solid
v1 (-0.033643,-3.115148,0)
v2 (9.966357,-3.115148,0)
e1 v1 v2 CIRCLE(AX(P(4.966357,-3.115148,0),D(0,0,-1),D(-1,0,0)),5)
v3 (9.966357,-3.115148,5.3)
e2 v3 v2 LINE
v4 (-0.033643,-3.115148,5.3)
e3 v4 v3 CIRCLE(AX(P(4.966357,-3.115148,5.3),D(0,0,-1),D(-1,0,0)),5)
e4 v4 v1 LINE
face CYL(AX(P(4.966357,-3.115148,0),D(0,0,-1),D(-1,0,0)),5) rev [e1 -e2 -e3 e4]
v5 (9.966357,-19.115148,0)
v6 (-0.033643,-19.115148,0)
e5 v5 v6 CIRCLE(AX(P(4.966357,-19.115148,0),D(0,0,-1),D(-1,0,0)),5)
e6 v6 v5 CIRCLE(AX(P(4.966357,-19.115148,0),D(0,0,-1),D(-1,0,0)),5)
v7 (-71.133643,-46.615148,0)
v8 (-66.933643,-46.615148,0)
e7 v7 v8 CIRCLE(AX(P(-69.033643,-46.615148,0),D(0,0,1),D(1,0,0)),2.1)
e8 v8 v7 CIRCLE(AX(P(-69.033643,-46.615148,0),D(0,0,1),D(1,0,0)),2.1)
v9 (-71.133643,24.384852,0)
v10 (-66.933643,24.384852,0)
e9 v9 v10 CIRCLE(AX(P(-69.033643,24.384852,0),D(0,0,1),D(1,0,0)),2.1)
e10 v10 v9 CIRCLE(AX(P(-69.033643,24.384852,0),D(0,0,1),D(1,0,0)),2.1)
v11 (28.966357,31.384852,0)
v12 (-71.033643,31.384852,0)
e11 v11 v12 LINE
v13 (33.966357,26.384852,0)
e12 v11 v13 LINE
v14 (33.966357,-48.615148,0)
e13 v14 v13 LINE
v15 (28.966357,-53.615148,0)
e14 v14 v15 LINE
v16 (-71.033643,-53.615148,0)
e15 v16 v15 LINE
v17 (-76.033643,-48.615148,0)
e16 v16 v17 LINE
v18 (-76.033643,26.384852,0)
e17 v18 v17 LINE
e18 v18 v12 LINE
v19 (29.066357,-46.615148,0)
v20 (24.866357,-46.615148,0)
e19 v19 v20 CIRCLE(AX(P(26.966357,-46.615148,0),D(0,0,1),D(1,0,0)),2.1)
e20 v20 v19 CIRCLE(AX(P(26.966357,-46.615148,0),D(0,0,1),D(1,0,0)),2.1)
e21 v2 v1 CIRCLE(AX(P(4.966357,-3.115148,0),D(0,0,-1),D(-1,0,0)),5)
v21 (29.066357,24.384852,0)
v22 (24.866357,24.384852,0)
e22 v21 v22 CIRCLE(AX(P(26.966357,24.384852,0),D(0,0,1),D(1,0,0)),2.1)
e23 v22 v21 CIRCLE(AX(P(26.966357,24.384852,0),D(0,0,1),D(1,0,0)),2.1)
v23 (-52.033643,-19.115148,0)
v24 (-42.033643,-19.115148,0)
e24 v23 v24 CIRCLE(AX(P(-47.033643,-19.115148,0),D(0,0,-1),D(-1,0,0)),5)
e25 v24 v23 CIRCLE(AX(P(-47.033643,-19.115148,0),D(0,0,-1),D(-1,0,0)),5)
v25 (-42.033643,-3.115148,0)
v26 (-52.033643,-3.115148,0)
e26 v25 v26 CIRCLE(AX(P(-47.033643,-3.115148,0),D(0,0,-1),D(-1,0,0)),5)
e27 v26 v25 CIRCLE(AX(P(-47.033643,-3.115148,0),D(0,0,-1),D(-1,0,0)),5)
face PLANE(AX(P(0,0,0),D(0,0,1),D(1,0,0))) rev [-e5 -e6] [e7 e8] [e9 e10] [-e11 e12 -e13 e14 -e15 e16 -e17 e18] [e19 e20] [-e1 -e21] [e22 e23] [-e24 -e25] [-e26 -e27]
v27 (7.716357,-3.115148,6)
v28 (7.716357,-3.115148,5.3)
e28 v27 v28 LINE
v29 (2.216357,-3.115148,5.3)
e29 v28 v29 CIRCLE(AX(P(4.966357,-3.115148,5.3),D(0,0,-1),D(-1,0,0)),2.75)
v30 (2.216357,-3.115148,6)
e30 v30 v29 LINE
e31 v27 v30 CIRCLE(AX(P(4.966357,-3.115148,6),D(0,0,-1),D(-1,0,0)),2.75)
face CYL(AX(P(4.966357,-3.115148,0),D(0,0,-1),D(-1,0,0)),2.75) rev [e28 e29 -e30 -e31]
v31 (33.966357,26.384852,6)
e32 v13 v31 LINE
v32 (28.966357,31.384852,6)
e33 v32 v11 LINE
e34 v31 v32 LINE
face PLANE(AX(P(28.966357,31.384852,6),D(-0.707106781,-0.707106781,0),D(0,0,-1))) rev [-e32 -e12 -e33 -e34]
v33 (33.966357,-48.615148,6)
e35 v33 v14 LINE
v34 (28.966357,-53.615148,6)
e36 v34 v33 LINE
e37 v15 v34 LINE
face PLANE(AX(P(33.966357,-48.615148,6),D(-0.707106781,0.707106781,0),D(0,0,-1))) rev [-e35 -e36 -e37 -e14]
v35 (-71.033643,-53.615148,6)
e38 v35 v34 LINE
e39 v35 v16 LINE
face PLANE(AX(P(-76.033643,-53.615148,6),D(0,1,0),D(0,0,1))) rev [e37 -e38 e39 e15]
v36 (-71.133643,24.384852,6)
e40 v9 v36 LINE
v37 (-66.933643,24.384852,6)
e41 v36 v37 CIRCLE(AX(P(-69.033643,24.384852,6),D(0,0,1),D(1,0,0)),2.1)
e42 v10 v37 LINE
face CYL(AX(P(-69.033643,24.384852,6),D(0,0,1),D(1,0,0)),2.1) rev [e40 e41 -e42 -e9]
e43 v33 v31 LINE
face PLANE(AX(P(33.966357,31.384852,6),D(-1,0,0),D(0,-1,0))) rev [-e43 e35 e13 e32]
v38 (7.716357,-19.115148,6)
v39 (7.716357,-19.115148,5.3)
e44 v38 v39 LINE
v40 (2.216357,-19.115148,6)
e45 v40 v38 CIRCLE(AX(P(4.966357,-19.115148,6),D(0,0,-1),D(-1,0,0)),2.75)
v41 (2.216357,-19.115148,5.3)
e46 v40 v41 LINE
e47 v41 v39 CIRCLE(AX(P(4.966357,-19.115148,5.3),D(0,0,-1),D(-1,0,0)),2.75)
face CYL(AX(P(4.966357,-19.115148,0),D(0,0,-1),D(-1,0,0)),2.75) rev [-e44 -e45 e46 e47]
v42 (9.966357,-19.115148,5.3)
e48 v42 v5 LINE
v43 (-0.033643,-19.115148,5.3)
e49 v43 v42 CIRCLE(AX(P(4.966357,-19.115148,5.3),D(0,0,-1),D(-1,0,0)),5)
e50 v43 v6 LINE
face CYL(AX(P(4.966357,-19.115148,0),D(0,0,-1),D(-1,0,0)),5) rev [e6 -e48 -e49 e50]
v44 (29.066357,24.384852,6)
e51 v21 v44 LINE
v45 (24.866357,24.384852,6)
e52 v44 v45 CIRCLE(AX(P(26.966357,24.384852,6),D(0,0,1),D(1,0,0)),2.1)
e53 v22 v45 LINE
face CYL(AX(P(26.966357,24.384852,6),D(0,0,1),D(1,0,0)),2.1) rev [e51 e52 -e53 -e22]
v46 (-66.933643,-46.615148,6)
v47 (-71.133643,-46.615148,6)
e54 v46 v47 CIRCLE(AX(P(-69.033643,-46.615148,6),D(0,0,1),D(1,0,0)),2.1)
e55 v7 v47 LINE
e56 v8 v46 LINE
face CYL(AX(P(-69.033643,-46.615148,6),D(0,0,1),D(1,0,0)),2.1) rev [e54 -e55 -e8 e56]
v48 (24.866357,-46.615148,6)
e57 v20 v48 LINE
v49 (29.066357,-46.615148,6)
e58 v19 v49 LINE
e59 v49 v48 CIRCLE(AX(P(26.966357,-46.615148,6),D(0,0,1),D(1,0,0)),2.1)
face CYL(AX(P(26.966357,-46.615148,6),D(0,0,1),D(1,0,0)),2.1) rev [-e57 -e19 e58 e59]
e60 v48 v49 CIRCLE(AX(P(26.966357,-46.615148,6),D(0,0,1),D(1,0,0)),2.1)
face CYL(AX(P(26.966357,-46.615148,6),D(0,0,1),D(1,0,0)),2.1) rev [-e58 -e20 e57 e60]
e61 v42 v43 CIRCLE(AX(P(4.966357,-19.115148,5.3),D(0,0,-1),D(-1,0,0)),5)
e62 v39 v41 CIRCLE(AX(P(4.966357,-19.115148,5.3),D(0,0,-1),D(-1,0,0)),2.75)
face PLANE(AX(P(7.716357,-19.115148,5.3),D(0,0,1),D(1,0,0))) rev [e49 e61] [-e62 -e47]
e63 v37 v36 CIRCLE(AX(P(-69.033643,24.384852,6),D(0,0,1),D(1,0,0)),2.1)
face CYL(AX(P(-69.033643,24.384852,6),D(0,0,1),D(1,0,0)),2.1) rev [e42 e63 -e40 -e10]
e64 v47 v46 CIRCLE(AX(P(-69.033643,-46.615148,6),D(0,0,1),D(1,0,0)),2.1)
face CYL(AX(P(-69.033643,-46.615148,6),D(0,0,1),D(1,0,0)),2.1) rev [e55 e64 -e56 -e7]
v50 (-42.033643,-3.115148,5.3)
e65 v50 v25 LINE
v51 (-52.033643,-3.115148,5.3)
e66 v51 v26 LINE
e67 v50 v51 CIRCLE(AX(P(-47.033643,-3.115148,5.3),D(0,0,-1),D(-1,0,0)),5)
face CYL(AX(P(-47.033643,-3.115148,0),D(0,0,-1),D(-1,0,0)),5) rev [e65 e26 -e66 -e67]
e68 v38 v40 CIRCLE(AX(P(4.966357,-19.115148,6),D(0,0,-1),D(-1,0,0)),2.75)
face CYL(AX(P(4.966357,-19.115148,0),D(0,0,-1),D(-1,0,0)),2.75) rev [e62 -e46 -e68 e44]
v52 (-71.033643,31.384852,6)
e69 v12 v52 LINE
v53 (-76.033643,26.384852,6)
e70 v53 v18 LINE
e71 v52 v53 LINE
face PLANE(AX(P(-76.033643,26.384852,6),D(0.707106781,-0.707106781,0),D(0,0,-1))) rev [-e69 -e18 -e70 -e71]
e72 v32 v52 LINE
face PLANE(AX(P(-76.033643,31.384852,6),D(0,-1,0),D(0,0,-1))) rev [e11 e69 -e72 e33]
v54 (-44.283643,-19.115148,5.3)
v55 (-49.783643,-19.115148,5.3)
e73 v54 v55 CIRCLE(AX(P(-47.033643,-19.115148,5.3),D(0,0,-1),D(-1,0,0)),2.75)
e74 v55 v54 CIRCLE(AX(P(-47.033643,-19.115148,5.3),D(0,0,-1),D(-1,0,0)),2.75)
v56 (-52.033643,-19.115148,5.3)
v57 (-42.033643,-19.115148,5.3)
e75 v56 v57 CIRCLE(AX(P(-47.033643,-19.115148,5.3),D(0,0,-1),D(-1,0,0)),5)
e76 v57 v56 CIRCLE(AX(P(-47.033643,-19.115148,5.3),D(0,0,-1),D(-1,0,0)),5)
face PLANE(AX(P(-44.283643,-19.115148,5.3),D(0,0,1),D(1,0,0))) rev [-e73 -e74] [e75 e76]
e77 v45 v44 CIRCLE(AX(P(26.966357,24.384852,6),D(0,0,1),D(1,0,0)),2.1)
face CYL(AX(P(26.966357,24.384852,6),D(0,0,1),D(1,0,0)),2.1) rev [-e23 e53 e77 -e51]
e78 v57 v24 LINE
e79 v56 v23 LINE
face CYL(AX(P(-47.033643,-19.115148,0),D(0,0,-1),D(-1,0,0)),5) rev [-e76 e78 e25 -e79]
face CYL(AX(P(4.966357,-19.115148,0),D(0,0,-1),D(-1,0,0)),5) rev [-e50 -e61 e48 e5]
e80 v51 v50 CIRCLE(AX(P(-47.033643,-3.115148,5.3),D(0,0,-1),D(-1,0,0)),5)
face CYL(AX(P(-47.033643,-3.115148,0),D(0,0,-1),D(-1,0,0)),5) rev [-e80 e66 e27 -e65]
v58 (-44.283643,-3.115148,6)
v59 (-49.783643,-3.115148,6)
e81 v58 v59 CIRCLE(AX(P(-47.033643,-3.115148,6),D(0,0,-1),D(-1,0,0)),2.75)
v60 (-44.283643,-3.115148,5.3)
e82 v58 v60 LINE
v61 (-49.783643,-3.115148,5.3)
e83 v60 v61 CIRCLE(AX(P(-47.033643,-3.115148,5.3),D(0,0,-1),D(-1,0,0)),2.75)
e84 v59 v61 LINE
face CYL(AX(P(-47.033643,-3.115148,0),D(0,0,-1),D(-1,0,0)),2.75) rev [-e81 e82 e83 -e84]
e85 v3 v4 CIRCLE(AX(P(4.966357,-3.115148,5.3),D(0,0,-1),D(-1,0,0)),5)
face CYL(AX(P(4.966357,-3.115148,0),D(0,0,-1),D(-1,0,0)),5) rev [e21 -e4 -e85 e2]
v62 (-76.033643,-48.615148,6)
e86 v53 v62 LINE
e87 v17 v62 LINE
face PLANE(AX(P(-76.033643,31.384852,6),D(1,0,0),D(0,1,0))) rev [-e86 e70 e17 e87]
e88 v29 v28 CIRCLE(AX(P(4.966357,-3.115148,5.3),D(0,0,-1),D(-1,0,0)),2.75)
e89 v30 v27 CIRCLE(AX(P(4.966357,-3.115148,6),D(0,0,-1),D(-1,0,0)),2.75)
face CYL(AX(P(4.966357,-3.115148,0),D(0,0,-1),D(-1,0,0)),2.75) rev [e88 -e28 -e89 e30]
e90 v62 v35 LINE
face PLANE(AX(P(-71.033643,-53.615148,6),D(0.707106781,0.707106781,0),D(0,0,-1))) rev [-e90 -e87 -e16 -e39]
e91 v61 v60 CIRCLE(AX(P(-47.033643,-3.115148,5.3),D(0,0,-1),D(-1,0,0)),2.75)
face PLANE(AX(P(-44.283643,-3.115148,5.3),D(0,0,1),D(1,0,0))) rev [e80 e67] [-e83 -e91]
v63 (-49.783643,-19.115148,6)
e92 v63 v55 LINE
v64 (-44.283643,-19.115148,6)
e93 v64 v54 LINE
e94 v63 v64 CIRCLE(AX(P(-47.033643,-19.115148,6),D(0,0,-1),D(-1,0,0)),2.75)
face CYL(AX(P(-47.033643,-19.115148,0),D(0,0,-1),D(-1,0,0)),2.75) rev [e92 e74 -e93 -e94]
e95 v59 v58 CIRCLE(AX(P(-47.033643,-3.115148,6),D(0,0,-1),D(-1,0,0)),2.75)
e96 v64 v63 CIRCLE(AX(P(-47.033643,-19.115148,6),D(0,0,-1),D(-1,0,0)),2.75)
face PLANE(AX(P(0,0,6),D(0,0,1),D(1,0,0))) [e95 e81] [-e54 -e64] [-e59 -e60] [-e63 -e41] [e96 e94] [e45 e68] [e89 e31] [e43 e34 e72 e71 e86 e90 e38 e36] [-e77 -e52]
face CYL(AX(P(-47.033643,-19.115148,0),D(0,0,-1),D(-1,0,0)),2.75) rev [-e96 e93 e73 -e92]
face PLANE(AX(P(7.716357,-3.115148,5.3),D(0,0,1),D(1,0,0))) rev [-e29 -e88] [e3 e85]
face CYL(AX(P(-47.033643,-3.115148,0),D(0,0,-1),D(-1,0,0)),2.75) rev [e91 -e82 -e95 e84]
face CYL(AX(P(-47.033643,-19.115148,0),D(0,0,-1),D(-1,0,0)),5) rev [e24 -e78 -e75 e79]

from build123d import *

# Parameters (mm, degrees)
SKETCH_1_W                = 110
SKETCH_1_H                = 85
EXTRUDE_1_DEPTH           = 6
CHAMFER_1_SIZE            = 5
HOLE_WIZARD_1_D           = 5.5
HOLE_WIZARD_1_CBORE_D     = 10
HOLE_WIZARD_1_CBORE_DEPTH = 5.3
HOLE_WIZARD_M5_1_D        = 4.2
HOLE_WIZARD_M5_1_DEPTH    = 12.4
HOLE_WIZARD_M5_1_TIP      = 1.2618073


with BuildPart() as part:
    # 草图1 → 凸台-拉伸1 (new body)
    with BuildSketch(Plane.XY):
        with Locations((-21.033643231, -11.115148183)):
            Rectangle(SKETCH_1_W, SKETCH_1_H)
    extrude(amount=EXTRUDE_1_DEPTH)

    # 倒角1
    chamfer_1_edges = [part.edges().sort_by_distance(p)[0] for p in [
        (-76.033643231, 31.384851817, 3),
        (33.966356769, 31.384851817, 3),
        (33.966356769, -53.615148183, 3),
        (-76.033643231, -53.615148183, 3),
    ]]
    chamfer(chamfer_1_edges, length=CHAMFER_1_SIZE)

    # 打孔尺寸根据内六角圆柱头螺钉的类型1 (through all)
    with Locations(Plane(origin=(0, 0, 0), x_dir=(-1, 0, 0), z_dir=(0, 0, -1))):
        with Locations((47.033643231, -19.115148183), (-4.966356769, -19.115148183), (-4.966356769, -3.115148183), (47.033643231, -3.115148183)):
            CounterBoreHole(HOLE_WIZARD_1_D / 2, HOLE_WIZARD_1_CBORE_D / 2, HOLE_WIZARD_1_CBORE_DEPTH)

    # M5 螺纹孔1
    with Locations(Plane.XY.offset(6)):
        with Locations((-69.033643231, 24.384851817), (26.966356769, 24.384851817), (26.966356769, -46.615148183), (-69.033643231, -46.615148183)):
            Hole(HOLE_WIZARD_M5_1_D / 2, depth=HOLE_WIZARD_M5_1_DEPTH)
            with Locations((0, 0, -(HOLE_WIZARD_M5_1_DEPTH + HOLE_WIZARD_M5_1_TIP / 2))):  # 118° drill point
                Cone(0, HOLE_WIZARD_M5_1_D / 2, HOLE_WIZARD_M5_1_TIP, mode=Mode.SUBTRACT)


solid = part.part
